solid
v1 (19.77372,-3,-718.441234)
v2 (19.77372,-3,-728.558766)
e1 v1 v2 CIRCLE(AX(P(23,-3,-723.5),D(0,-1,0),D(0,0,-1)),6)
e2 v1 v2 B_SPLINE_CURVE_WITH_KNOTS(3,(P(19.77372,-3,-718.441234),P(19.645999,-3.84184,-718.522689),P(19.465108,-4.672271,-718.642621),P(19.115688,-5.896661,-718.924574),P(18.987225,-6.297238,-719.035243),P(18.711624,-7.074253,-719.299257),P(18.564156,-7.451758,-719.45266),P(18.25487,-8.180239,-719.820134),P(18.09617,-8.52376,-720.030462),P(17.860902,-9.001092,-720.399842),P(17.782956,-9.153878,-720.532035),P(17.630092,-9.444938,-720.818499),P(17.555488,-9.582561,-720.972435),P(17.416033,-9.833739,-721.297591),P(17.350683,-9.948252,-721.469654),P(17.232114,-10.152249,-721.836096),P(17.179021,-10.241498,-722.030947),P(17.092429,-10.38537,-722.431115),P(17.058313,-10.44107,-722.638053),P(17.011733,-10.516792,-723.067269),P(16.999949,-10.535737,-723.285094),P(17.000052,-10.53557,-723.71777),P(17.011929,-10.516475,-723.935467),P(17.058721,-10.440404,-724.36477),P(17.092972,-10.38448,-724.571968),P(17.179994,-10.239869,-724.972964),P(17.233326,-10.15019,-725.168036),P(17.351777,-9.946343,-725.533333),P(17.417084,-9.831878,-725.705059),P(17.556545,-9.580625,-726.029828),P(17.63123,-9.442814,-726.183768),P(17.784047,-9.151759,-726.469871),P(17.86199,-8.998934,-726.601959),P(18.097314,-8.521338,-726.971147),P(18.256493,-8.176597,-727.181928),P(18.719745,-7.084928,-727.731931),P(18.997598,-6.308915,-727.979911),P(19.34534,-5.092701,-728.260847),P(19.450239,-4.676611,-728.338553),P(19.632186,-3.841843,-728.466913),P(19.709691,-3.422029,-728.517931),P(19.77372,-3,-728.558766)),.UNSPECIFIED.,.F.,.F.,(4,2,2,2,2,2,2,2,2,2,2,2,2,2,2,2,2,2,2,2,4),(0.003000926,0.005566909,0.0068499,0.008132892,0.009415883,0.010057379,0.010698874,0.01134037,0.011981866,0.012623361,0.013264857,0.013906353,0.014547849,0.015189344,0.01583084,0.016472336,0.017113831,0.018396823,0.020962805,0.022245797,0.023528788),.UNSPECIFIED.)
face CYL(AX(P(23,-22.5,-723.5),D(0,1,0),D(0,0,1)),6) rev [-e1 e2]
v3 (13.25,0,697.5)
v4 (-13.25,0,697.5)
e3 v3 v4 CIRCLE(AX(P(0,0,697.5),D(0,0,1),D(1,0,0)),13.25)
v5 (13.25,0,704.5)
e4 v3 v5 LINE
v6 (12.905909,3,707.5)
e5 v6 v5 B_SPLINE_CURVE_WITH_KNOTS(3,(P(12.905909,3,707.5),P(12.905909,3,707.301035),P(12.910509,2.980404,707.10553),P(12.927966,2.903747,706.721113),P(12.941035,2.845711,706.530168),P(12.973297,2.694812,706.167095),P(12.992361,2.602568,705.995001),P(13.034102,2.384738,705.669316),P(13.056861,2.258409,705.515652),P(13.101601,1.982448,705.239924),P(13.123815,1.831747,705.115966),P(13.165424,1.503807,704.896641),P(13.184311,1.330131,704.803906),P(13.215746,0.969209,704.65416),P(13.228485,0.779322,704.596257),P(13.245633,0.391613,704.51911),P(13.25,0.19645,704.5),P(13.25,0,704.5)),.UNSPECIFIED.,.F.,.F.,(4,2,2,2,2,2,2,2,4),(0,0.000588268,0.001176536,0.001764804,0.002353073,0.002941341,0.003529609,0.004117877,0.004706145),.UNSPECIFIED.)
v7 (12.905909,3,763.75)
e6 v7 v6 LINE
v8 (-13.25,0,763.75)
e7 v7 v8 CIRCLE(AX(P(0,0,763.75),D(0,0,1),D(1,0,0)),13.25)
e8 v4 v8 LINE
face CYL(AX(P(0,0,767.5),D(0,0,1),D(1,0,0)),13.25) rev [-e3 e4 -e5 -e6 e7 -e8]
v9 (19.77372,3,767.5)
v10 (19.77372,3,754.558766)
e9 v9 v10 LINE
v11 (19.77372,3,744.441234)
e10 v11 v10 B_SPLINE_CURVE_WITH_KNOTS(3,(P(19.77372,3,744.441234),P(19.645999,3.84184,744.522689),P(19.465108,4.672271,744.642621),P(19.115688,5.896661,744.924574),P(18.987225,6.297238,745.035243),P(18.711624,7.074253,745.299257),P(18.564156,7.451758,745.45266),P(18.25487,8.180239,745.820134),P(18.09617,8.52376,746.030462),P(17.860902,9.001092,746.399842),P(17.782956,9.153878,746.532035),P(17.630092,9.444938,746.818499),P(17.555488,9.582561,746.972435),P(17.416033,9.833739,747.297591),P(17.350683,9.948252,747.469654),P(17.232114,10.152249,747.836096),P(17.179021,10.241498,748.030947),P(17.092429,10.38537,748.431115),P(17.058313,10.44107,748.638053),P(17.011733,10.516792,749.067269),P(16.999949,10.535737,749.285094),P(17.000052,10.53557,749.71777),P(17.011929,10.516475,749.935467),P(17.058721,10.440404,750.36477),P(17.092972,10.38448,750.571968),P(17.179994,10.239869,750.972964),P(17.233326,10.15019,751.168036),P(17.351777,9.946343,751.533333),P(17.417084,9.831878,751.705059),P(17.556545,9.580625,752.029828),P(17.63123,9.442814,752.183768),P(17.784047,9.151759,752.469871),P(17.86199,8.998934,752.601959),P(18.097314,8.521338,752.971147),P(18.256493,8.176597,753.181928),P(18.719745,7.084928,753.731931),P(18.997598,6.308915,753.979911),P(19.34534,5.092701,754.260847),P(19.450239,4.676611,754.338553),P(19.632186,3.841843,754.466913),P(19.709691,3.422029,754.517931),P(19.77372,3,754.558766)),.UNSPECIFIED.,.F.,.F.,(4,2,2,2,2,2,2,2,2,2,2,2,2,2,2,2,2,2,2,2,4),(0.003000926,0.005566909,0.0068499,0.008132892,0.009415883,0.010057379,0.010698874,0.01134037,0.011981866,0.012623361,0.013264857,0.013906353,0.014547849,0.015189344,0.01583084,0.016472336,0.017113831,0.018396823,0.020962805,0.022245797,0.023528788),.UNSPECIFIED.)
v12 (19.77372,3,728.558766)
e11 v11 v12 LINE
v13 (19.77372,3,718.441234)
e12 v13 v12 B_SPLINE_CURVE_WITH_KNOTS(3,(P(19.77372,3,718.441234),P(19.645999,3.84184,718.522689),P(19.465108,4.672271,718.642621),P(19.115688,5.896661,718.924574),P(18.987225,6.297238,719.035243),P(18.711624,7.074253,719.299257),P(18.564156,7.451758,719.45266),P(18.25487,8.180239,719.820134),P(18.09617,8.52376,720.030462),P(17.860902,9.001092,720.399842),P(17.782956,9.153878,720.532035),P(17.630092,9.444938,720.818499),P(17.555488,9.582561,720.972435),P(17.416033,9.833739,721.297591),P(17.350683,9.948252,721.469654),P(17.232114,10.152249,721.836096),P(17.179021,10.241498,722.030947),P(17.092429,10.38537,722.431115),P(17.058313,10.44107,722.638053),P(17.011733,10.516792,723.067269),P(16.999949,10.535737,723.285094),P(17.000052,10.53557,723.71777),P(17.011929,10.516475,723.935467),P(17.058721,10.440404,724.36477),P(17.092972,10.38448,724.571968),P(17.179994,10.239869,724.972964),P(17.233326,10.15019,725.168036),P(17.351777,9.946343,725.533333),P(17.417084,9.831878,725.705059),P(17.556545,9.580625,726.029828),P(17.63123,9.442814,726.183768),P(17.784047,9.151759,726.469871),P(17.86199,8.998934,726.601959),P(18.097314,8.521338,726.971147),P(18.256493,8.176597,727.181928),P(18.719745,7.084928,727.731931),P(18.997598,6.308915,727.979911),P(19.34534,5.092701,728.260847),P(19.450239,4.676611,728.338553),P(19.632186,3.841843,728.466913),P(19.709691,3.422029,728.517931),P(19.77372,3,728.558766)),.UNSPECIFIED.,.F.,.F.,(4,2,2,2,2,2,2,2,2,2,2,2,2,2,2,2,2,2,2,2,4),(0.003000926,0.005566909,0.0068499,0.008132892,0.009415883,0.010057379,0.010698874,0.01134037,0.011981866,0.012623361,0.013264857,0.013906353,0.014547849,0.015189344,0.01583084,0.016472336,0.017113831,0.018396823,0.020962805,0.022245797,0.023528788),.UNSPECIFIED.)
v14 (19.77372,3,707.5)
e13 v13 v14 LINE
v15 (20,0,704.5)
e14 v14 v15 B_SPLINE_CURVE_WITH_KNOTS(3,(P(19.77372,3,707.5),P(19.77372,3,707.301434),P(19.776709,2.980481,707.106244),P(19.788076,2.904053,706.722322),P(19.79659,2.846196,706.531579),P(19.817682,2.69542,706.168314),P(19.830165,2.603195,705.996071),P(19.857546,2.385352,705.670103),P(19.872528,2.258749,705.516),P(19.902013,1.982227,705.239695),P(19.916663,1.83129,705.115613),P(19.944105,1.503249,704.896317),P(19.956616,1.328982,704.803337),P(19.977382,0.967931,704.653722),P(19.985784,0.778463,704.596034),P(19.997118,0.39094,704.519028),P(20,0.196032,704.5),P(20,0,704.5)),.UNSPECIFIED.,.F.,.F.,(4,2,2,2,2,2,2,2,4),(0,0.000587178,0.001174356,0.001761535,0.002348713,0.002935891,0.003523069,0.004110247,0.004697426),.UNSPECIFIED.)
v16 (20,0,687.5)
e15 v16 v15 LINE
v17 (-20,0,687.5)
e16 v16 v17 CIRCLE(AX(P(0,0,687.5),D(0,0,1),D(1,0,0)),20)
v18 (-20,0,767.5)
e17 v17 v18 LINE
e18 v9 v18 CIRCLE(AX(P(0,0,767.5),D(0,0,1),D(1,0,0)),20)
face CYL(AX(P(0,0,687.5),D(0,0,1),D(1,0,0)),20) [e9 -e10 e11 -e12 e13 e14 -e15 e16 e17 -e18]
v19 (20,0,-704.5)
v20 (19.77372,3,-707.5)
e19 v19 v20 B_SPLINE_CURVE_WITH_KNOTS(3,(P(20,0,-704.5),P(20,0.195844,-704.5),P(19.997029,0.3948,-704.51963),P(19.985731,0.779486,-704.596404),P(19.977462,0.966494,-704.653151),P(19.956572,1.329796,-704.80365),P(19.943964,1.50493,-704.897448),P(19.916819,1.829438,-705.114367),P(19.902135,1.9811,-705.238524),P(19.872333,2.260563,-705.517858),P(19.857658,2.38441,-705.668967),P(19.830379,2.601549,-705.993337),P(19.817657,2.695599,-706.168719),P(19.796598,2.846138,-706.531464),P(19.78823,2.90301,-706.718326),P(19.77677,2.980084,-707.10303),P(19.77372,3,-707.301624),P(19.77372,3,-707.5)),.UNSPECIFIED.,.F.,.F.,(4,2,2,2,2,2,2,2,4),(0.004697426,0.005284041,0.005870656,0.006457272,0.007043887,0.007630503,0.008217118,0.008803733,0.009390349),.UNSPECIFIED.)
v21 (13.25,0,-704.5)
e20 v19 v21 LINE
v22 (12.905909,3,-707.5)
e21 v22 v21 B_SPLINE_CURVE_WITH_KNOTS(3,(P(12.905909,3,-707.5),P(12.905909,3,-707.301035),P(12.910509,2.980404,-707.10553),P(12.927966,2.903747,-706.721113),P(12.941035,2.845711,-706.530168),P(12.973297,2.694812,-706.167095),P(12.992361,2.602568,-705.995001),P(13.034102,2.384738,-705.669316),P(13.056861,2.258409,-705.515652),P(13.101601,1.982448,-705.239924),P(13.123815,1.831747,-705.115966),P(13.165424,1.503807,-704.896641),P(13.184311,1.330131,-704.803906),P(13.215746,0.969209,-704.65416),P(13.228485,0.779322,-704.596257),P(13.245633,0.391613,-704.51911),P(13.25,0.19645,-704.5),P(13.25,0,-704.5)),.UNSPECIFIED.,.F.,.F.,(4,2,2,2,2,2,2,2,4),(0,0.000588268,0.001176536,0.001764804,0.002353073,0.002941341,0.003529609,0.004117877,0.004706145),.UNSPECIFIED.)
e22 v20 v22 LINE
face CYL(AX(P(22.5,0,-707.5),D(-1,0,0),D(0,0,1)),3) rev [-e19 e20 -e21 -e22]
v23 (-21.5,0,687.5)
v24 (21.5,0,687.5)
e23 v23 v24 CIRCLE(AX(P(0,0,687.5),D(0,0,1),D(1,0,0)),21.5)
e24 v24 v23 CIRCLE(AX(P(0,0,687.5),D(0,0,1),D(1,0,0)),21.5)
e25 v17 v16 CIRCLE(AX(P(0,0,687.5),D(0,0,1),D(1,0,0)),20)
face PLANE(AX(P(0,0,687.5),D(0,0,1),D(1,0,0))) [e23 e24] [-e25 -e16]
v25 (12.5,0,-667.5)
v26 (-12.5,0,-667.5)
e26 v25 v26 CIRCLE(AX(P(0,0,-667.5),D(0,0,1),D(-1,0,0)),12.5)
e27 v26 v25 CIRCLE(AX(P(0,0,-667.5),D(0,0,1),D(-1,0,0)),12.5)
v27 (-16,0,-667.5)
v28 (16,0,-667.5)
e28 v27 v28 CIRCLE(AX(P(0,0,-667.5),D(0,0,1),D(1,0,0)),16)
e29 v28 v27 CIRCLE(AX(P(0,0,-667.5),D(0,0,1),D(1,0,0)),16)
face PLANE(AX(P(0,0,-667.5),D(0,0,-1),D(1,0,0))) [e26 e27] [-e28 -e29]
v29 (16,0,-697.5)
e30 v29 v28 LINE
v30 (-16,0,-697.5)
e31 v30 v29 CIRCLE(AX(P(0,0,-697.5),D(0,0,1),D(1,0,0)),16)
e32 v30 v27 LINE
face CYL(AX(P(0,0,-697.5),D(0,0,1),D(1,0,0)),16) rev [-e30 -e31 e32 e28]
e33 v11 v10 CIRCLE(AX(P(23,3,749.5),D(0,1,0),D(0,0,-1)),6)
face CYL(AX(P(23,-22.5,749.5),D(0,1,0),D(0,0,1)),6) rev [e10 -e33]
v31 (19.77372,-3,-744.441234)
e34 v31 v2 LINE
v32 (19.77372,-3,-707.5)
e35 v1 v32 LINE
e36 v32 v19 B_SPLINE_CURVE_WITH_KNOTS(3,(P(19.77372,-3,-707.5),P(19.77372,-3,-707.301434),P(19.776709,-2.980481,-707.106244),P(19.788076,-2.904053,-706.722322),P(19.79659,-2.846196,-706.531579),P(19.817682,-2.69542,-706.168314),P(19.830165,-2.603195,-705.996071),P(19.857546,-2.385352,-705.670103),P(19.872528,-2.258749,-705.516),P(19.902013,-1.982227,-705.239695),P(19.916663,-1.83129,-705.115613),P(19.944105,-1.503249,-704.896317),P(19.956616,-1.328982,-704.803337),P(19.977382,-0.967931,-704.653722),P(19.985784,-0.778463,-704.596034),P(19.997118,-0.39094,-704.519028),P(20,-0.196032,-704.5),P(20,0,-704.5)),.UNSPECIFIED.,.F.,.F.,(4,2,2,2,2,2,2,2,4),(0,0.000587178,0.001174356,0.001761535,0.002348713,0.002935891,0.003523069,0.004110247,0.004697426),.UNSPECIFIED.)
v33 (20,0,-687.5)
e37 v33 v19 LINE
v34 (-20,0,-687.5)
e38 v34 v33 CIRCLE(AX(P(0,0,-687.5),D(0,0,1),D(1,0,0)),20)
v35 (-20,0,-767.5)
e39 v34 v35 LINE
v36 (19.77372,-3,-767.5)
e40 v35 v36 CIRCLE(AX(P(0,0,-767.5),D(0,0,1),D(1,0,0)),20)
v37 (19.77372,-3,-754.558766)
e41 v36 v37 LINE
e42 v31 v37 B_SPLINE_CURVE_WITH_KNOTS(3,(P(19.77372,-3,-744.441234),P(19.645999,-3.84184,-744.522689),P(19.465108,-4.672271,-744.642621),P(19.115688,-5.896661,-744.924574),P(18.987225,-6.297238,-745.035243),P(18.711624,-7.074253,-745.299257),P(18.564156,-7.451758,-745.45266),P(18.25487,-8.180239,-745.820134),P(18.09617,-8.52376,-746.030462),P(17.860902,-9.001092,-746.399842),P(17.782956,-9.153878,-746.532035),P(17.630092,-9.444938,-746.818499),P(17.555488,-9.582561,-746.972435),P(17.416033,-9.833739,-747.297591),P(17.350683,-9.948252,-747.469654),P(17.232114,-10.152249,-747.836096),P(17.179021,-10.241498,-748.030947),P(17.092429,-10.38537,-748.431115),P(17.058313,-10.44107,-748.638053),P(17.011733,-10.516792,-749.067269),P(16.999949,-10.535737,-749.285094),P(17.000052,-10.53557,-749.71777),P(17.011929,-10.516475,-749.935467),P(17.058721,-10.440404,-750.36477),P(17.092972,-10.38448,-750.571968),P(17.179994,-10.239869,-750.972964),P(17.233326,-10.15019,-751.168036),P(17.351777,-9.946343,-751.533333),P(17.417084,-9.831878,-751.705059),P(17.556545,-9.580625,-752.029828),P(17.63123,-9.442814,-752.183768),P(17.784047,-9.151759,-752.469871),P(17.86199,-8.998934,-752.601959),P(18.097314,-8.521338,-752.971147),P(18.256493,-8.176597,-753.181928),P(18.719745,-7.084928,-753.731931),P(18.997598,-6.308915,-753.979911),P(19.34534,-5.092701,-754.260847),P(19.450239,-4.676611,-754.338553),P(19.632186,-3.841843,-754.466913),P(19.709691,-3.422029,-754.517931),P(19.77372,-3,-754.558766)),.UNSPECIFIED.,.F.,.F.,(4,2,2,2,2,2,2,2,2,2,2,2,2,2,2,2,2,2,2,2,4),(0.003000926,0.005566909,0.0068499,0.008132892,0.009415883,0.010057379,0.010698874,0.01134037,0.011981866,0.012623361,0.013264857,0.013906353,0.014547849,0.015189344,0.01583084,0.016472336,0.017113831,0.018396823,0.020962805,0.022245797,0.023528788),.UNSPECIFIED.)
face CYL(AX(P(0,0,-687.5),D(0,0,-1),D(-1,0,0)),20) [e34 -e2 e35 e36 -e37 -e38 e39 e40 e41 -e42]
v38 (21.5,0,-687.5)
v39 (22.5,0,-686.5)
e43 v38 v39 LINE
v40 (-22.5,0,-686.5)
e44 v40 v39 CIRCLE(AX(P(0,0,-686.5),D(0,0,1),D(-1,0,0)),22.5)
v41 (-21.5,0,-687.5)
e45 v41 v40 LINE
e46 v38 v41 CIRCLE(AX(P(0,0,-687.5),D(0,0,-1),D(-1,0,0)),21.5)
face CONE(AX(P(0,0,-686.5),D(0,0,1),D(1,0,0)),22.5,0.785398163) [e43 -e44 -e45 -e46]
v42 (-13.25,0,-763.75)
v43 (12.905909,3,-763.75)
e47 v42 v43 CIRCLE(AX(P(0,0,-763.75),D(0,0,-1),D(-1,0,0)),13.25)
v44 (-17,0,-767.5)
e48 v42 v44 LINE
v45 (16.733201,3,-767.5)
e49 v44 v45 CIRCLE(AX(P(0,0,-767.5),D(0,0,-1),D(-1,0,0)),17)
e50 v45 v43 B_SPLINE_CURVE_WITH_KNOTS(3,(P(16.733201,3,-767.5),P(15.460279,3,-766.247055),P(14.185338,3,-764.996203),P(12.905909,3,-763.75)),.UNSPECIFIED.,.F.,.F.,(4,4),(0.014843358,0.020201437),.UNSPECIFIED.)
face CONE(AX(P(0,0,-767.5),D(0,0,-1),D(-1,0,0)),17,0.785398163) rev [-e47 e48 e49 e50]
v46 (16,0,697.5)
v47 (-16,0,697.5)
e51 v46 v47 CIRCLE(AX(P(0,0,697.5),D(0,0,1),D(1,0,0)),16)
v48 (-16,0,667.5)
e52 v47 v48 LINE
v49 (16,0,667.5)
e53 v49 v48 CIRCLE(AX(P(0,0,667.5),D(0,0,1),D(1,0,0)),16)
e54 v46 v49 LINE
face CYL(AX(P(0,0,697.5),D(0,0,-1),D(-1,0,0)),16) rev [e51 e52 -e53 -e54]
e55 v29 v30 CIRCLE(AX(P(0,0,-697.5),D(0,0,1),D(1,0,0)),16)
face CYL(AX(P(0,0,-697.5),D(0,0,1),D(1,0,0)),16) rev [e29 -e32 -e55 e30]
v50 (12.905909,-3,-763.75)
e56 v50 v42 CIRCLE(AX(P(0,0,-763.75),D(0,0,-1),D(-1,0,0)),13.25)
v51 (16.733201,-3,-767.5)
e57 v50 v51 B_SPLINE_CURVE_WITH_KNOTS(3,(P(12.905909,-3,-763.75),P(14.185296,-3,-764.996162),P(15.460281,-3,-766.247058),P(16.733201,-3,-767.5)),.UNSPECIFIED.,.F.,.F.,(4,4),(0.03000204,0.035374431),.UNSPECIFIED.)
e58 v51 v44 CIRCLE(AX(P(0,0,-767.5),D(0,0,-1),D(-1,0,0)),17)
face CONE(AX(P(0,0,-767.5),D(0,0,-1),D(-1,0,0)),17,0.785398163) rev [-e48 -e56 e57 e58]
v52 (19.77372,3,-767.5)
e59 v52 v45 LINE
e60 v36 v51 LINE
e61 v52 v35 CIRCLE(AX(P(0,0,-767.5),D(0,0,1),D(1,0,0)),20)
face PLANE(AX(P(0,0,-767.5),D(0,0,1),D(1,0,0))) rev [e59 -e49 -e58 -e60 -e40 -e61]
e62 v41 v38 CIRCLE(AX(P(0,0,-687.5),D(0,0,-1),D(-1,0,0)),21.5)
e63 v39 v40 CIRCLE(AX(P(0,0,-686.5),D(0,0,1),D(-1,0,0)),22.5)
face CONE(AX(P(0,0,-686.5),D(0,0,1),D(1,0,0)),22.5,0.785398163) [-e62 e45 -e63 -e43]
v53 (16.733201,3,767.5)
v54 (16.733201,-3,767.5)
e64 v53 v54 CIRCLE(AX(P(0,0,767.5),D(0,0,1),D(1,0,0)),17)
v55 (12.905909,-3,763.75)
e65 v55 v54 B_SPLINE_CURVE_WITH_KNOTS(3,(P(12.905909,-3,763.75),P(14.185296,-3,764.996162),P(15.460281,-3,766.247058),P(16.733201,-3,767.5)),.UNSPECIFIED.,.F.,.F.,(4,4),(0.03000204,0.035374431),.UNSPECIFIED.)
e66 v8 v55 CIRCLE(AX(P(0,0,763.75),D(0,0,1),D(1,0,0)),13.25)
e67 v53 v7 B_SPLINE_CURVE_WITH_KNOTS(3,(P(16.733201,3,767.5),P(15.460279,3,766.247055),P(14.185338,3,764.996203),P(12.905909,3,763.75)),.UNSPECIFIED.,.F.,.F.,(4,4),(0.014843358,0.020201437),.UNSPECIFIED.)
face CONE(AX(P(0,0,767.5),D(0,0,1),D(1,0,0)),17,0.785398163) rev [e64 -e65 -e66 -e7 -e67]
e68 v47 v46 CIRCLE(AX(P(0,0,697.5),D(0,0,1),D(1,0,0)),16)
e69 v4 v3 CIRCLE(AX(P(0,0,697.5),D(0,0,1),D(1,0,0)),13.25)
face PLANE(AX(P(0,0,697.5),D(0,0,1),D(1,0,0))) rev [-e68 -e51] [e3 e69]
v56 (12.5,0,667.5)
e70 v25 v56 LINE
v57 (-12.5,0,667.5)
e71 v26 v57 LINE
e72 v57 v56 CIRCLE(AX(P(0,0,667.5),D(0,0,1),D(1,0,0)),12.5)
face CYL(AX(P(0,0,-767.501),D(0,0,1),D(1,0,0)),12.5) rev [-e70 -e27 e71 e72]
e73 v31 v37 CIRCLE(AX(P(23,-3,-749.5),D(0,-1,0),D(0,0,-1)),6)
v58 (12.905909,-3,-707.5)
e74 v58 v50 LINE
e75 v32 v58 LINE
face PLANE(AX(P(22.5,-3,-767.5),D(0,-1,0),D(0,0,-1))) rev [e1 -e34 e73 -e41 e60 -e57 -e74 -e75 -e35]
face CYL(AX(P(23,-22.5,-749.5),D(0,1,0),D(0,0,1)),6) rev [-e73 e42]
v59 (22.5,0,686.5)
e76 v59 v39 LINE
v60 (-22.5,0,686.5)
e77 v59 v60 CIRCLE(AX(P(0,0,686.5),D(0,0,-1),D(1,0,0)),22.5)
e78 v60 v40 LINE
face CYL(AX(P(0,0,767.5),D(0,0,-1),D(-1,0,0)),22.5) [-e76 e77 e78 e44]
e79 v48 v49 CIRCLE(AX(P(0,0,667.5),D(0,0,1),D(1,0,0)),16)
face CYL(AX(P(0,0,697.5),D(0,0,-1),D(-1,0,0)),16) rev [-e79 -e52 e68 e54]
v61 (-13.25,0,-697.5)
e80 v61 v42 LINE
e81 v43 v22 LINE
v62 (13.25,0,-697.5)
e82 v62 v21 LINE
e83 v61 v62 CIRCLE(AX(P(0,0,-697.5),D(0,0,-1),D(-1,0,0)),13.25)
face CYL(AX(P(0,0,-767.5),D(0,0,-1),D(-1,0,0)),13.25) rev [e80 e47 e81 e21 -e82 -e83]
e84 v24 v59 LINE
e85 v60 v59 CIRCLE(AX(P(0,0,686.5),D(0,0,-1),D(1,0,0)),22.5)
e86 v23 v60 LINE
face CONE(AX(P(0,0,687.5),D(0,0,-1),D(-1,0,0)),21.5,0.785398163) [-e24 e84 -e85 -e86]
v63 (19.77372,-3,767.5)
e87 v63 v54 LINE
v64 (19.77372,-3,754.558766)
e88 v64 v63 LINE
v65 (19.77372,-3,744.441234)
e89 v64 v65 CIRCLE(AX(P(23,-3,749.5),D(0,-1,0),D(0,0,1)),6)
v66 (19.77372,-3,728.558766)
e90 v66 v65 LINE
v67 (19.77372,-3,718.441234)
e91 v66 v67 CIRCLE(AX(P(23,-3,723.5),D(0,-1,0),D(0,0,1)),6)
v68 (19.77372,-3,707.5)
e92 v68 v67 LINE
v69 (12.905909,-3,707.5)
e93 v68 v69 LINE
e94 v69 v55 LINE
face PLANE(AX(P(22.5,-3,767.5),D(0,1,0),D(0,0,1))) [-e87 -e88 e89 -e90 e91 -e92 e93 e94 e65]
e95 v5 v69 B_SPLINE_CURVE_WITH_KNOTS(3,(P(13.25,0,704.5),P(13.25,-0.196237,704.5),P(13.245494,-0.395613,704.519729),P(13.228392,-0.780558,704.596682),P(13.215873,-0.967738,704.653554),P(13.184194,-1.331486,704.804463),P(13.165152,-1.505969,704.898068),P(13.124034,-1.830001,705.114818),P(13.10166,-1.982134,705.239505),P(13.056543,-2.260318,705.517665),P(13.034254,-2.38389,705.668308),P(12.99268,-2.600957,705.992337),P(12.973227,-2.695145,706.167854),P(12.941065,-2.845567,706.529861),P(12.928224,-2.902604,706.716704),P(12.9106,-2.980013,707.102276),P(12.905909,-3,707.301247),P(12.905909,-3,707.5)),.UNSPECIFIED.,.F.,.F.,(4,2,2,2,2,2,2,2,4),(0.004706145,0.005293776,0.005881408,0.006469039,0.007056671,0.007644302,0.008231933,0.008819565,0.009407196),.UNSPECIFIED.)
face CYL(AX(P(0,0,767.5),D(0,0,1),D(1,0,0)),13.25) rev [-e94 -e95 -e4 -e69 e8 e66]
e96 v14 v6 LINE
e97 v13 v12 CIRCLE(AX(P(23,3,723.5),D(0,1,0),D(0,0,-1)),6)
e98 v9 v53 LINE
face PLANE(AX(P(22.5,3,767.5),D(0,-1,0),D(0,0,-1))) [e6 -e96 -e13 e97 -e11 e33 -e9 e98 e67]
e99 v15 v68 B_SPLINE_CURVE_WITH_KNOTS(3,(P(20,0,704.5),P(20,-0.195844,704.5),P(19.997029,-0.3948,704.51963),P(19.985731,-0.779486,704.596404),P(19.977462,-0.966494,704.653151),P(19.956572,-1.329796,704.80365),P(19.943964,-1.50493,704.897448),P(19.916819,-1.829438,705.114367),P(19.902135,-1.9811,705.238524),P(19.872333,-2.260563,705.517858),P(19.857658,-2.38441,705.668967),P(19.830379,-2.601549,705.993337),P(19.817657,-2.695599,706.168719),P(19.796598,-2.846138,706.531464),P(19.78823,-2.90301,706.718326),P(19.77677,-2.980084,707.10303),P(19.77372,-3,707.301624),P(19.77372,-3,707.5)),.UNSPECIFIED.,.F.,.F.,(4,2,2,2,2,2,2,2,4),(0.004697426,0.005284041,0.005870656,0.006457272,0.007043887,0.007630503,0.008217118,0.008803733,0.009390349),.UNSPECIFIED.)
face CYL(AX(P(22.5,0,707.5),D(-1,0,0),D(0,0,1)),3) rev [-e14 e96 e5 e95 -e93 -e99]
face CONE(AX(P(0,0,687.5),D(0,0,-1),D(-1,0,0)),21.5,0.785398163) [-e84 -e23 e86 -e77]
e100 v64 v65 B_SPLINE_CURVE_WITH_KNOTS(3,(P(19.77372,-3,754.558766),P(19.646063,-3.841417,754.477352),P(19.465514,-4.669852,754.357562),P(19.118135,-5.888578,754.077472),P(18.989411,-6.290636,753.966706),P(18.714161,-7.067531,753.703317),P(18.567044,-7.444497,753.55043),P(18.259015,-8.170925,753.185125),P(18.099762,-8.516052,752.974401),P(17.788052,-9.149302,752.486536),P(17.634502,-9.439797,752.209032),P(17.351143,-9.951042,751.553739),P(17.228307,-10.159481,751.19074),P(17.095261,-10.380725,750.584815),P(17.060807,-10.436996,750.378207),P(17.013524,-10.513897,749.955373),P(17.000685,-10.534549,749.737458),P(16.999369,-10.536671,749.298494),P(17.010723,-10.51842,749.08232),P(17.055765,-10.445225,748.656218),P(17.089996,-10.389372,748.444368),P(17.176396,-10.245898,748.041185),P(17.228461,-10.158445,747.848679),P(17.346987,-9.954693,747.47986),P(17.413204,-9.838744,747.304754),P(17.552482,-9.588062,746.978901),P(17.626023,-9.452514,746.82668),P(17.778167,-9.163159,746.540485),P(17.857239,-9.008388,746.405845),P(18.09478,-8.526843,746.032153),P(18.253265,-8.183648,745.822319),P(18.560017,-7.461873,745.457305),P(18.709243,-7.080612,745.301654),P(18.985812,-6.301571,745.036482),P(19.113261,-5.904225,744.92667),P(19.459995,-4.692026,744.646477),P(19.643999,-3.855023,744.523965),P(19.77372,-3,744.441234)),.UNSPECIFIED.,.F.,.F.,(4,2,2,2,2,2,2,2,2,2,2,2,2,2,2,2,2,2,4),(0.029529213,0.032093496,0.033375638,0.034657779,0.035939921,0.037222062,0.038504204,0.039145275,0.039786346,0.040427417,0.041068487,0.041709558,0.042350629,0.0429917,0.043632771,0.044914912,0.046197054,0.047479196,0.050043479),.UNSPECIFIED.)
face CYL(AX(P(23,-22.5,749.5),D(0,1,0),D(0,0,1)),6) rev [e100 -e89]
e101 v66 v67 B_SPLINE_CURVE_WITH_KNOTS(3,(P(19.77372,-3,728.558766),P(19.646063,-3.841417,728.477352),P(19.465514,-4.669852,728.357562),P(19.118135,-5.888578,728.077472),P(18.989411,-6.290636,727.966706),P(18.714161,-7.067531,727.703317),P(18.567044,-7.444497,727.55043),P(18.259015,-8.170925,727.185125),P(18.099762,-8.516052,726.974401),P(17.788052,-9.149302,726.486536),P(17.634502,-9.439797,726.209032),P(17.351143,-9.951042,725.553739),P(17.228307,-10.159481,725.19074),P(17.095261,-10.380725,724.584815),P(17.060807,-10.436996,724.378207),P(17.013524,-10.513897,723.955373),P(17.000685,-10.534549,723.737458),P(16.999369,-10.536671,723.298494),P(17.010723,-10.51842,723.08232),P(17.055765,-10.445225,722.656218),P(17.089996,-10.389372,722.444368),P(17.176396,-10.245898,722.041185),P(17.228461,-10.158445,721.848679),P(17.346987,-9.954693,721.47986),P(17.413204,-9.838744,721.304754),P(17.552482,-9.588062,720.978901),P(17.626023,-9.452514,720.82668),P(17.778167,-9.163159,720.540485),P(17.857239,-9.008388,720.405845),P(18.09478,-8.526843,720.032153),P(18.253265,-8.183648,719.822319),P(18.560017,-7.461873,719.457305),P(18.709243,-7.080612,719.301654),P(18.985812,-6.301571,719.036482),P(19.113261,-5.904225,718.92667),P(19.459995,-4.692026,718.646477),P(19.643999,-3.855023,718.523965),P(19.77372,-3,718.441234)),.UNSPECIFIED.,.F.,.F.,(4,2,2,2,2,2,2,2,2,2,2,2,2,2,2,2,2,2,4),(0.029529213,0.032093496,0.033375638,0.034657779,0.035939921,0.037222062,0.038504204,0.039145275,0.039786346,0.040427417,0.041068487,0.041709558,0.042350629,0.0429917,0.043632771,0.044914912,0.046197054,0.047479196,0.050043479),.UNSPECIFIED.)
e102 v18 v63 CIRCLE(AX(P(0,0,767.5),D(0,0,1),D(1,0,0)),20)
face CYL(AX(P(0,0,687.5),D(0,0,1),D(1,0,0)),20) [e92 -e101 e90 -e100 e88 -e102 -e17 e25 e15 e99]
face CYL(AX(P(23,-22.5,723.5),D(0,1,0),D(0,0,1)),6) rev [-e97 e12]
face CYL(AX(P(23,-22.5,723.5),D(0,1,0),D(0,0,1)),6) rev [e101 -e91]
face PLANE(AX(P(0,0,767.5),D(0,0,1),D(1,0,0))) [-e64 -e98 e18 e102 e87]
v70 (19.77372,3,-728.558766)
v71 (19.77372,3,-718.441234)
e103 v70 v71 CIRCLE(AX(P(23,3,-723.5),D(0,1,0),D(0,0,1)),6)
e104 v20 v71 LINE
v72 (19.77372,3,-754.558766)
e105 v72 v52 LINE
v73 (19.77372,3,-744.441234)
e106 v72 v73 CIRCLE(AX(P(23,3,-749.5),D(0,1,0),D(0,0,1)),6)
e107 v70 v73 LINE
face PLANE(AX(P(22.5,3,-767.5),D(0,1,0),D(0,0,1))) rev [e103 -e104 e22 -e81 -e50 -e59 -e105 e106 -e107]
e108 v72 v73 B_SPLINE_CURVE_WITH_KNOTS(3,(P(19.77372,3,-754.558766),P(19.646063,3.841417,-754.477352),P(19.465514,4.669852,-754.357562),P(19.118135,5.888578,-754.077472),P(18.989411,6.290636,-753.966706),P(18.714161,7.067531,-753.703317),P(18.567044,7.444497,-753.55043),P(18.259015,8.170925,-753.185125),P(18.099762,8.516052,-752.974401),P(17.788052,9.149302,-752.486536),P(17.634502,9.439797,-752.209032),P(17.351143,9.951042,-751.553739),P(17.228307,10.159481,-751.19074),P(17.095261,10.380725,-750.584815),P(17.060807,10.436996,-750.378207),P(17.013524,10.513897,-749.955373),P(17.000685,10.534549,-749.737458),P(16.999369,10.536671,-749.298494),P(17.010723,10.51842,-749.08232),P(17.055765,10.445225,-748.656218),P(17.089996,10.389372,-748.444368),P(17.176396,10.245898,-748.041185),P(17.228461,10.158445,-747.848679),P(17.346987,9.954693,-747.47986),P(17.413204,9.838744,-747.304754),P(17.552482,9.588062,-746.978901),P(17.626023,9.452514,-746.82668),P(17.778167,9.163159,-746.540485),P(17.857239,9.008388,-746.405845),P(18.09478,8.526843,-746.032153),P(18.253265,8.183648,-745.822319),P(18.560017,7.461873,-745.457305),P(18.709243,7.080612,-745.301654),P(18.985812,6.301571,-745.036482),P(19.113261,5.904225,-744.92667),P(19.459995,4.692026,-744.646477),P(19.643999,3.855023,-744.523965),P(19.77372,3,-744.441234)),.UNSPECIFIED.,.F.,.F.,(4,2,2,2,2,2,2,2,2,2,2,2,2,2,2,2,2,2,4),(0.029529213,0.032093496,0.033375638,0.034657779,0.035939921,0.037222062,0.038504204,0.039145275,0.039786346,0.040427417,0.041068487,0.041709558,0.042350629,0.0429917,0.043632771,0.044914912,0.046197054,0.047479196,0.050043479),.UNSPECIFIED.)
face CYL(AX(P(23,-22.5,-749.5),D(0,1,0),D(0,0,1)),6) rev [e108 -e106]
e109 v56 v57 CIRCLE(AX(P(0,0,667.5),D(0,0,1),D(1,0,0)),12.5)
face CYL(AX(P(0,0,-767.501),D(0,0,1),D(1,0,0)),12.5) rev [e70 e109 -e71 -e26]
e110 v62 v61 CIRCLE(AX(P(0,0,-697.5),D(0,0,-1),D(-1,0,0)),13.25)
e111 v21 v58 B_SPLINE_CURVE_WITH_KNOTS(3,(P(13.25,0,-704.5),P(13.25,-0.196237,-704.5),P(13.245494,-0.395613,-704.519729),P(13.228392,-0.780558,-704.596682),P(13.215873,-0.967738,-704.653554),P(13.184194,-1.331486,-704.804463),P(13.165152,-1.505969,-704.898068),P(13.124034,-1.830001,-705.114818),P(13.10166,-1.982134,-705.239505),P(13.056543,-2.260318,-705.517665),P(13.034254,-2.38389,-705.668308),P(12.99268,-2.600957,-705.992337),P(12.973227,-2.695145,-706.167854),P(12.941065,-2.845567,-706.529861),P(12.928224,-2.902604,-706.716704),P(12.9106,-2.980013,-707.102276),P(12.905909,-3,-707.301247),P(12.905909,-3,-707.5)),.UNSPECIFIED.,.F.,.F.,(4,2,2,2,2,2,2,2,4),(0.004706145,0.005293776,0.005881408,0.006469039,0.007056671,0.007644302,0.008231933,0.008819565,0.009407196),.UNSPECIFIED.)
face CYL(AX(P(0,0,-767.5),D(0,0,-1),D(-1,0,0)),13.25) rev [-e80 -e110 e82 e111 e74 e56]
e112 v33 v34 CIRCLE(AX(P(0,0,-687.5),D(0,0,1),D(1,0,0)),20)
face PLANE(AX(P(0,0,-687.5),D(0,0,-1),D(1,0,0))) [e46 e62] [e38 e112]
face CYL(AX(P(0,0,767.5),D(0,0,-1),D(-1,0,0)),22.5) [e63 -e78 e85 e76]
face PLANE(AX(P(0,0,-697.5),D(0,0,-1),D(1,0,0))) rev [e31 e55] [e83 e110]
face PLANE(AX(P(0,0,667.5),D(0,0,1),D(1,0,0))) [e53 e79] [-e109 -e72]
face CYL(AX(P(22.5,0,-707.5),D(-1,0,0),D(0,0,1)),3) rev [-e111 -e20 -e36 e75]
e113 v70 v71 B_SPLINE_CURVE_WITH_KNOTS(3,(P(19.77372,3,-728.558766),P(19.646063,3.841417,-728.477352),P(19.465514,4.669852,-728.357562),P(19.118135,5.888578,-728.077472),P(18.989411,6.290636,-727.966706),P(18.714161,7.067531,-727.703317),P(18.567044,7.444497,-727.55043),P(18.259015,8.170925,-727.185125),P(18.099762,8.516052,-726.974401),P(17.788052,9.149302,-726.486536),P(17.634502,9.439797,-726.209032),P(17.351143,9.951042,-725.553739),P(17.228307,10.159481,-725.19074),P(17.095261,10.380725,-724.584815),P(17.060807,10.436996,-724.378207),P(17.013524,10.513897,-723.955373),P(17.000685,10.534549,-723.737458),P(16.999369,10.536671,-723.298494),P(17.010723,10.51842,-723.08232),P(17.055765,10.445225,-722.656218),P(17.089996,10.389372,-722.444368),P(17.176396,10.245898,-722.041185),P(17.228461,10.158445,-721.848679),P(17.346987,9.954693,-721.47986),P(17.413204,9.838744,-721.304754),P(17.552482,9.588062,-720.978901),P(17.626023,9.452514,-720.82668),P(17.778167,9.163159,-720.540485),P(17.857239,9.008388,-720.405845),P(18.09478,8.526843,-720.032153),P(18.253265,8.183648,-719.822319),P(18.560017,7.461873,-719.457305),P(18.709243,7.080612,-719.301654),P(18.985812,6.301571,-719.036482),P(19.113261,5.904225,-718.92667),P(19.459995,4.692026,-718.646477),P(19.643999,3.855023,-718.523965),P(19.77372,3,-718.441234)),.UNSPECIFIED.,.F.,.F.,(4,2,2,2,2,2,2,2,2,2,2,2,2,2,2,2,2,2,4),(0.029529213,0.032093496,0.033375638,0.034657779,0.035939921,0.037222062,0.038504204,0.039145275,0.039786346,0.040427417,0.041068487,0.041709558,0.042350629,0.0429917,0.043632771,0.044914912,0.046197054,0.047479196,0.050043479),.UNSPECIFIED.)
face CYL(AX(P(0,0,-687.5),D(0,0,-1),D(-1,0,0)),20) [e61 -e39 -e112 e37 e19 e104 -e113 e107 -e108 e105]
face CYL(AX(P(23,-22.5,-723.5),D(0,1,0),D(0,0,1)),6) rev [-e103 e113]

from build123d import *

# Parameters (mm, degrees)
SKETCH_2_R                    = 22.5
EXTRUDE_1_DEPTH               = 767.5
SKETCH_3_R                    = 22.5
SKETCH_3_R_2                  = 20
CUT_EXTRUDE_1_DEPTH           = 80
SKETCH_4_R                    = 16
CUT_EXTRUDE_2_DEPTH           = 30
CUT_EXTRUDE_3_REACH           = 1437.353
SKETCH_5_R                    = 12.5
HOLE_WIZARD_M30_1_D           = 26.5
HOLE_WIZARD_M30_1_DEPTH       = 70
HOLE_WIZARD_M30_1_CSINK_D     = 34
HOLE_WIZARD_M30_1_CSINK_ANGLE = 90
HOLE_WIZARD_M30_2_D           = 26.5
HOLE_WIZARD_M30_2_DEPTH       = 70
HOLE_WIZARD_M30_2_CSINK_D     = 34
HOLE_WIZARD_M30_2_CSINK_ANGLE = 90
SKETCH_10_R                   = 6
CUT_EXTRUDE_4_DEPTH           = 769.159325921
CUT_EXTRUDE_5_DEPTH           = 769.159326021
CHAMFER_1_SIZE                = 1


with BuildPart() as part:
    # 草图2 → 凸台-拉伸1 (new, symmetric)
    with BuildSketch(Plane.XY):
        Circle(SKETCH_2_R)
    extrude(amount=EXTRUDE_1_DEPTH, both=True)

    # 草图3 → 切除-拉伸1 (cut)
    with BuildSketch(Plane.XY.offset(767.5)):
        Circle(SKETCH_3_R)
        Circle(SKETCH_3_R_2, mode=Mode.SUBTRACT)
    cut_extrude_1 = extrude(amount=-CUT_EXTRUDE_1_DEPTH, mode=Mode.SUBTRACT)

    # 草图4 → 切除-拉伸2 (cut)
    with BuildSketch(Plane.XY.offset(667.5)):
        Circle(SKETCH_4_R)
    cut_extrude_2 = extrude(amount=CUT_EXTRUDE_2_DEPTH, mode=Mode.SUBTRACT)

    # 镜向1: 切除-拉伸1, 切除-拉伸2 across plane
    add(cut_extrude_1.mirror(Plane.XY), mode=Mode.SUBTRACT)
    add(cut_extrude_2.mirror(Plane.XY), mode=Mode.SUBTRACT)

    # 草图5 → 切除-拉伸3 (cut, up to next)
    with BuildSketch(Plane.XY.offset(667.5), mode=Mode.PRIVATE) as cut_extrude_3_sk1:
        Circle(SKETCH_5_R)
    cut_extrude_3_tool1 = extrude(cut_extrude_3_sk1.sketch, amount=-CUT_EXTRUDE_3_REACH, mode=Mode.PRIVATE) & part.part
    add(cut_extrude_3_tool1.solids().sort_by_distance((0, 0, 667.5))[0], mode=Mode.SUBTRACT)

    # M30 螺纹孔1
    with Locations(Plane.XY.offset(767.5)):
        with Locations((0, 0)):
            CounterSinkHole(HOLE_WIZARD_M30_1_D / 2, HOLE_WIZARD_M30_1_CSINK_D / 2, depth=HOLE_WIZARD_M30_1_DEPTH, counter_sink_angle=HOLE_WIZARD_M30_1_CSINK_ANGLE)

    # M30 螺纹孔2-左旋
    with Locations(Plane(origin=(0, 0, -767.5), x_dir=(-1, 0, 0), z_dir=(0, 0, -1))):
        with Locations((0, 0)):
            CounterSinkHole(HOLE_WIZARD_M30_2_D / 2, HOLE_WIZARD_M30_2_CSINK_D / 2, depth=HOLE_WIZARD_M30_2_DEPTH, counter_sink_angle=HOLE_WIZARD_M30_2_CSINK_ANGLE)

    # 草图10 → 切除-拉伸4 (cut, symmetric)
    with BuildSketch(Plane(origin=(0, 0, 0), x_dir=(1, 0, 0), z_dir=(0, 1, 0))):
        with Locations((23, -749.5)):
            Circle(SKETCH_10_R)
        with Locations((23, -723.5)):
            Circle(SKETCH_10_R)
    cut_extrude_4 = extrude(amount=CUT_EXTRUDE_4_DEPTH, both=True, mode=Mode.SUBTRACT)

    # 草图11 → 切除-拉伸5 (cut, through all)
    with BuildSketch(Plane(origin=(0, 0, 0), x_dir=(0, 0, -1), z_dir=(1, 0, 0))):
        with BuildLine():
            Line((-767.5, 3), (-707.5, 3))
            ThreePointArc((-707.5, 3), (-704.5, 0), (-707.5, -3))
            Line((-707.5, -3), (-767.5, -3))
            ThreePointArc((-767.5, -3), (-770.5, 0), (-767.5, 3))
        make_face()
    cut_extrude_5 = extrude(amount=CUT_EXTRUDE_5_DEPTH, mode=Mode.SUBTRACT)

    # 镜向2: 切除-拉伸4, 切除-拉伸5 across plane
    add(cut_extrude_4.mirror(Plane.XY), mode=Mode.SUBTRACT)
    add(cut_extrude_5.mirror(Plane.XY), mode=Mode.SUBTRACT)

    # 倒角1
    chamfer_1_edges = [part.edges().sort_by_distance(p)[0] for p in [
        (-22.5, 0, -687.5),
        (-22.5, 0, 687.5),
    ]]
    chamfer(chamfer_1_edges, length=CHAMFER_1_SIZE)


solid = part.part
